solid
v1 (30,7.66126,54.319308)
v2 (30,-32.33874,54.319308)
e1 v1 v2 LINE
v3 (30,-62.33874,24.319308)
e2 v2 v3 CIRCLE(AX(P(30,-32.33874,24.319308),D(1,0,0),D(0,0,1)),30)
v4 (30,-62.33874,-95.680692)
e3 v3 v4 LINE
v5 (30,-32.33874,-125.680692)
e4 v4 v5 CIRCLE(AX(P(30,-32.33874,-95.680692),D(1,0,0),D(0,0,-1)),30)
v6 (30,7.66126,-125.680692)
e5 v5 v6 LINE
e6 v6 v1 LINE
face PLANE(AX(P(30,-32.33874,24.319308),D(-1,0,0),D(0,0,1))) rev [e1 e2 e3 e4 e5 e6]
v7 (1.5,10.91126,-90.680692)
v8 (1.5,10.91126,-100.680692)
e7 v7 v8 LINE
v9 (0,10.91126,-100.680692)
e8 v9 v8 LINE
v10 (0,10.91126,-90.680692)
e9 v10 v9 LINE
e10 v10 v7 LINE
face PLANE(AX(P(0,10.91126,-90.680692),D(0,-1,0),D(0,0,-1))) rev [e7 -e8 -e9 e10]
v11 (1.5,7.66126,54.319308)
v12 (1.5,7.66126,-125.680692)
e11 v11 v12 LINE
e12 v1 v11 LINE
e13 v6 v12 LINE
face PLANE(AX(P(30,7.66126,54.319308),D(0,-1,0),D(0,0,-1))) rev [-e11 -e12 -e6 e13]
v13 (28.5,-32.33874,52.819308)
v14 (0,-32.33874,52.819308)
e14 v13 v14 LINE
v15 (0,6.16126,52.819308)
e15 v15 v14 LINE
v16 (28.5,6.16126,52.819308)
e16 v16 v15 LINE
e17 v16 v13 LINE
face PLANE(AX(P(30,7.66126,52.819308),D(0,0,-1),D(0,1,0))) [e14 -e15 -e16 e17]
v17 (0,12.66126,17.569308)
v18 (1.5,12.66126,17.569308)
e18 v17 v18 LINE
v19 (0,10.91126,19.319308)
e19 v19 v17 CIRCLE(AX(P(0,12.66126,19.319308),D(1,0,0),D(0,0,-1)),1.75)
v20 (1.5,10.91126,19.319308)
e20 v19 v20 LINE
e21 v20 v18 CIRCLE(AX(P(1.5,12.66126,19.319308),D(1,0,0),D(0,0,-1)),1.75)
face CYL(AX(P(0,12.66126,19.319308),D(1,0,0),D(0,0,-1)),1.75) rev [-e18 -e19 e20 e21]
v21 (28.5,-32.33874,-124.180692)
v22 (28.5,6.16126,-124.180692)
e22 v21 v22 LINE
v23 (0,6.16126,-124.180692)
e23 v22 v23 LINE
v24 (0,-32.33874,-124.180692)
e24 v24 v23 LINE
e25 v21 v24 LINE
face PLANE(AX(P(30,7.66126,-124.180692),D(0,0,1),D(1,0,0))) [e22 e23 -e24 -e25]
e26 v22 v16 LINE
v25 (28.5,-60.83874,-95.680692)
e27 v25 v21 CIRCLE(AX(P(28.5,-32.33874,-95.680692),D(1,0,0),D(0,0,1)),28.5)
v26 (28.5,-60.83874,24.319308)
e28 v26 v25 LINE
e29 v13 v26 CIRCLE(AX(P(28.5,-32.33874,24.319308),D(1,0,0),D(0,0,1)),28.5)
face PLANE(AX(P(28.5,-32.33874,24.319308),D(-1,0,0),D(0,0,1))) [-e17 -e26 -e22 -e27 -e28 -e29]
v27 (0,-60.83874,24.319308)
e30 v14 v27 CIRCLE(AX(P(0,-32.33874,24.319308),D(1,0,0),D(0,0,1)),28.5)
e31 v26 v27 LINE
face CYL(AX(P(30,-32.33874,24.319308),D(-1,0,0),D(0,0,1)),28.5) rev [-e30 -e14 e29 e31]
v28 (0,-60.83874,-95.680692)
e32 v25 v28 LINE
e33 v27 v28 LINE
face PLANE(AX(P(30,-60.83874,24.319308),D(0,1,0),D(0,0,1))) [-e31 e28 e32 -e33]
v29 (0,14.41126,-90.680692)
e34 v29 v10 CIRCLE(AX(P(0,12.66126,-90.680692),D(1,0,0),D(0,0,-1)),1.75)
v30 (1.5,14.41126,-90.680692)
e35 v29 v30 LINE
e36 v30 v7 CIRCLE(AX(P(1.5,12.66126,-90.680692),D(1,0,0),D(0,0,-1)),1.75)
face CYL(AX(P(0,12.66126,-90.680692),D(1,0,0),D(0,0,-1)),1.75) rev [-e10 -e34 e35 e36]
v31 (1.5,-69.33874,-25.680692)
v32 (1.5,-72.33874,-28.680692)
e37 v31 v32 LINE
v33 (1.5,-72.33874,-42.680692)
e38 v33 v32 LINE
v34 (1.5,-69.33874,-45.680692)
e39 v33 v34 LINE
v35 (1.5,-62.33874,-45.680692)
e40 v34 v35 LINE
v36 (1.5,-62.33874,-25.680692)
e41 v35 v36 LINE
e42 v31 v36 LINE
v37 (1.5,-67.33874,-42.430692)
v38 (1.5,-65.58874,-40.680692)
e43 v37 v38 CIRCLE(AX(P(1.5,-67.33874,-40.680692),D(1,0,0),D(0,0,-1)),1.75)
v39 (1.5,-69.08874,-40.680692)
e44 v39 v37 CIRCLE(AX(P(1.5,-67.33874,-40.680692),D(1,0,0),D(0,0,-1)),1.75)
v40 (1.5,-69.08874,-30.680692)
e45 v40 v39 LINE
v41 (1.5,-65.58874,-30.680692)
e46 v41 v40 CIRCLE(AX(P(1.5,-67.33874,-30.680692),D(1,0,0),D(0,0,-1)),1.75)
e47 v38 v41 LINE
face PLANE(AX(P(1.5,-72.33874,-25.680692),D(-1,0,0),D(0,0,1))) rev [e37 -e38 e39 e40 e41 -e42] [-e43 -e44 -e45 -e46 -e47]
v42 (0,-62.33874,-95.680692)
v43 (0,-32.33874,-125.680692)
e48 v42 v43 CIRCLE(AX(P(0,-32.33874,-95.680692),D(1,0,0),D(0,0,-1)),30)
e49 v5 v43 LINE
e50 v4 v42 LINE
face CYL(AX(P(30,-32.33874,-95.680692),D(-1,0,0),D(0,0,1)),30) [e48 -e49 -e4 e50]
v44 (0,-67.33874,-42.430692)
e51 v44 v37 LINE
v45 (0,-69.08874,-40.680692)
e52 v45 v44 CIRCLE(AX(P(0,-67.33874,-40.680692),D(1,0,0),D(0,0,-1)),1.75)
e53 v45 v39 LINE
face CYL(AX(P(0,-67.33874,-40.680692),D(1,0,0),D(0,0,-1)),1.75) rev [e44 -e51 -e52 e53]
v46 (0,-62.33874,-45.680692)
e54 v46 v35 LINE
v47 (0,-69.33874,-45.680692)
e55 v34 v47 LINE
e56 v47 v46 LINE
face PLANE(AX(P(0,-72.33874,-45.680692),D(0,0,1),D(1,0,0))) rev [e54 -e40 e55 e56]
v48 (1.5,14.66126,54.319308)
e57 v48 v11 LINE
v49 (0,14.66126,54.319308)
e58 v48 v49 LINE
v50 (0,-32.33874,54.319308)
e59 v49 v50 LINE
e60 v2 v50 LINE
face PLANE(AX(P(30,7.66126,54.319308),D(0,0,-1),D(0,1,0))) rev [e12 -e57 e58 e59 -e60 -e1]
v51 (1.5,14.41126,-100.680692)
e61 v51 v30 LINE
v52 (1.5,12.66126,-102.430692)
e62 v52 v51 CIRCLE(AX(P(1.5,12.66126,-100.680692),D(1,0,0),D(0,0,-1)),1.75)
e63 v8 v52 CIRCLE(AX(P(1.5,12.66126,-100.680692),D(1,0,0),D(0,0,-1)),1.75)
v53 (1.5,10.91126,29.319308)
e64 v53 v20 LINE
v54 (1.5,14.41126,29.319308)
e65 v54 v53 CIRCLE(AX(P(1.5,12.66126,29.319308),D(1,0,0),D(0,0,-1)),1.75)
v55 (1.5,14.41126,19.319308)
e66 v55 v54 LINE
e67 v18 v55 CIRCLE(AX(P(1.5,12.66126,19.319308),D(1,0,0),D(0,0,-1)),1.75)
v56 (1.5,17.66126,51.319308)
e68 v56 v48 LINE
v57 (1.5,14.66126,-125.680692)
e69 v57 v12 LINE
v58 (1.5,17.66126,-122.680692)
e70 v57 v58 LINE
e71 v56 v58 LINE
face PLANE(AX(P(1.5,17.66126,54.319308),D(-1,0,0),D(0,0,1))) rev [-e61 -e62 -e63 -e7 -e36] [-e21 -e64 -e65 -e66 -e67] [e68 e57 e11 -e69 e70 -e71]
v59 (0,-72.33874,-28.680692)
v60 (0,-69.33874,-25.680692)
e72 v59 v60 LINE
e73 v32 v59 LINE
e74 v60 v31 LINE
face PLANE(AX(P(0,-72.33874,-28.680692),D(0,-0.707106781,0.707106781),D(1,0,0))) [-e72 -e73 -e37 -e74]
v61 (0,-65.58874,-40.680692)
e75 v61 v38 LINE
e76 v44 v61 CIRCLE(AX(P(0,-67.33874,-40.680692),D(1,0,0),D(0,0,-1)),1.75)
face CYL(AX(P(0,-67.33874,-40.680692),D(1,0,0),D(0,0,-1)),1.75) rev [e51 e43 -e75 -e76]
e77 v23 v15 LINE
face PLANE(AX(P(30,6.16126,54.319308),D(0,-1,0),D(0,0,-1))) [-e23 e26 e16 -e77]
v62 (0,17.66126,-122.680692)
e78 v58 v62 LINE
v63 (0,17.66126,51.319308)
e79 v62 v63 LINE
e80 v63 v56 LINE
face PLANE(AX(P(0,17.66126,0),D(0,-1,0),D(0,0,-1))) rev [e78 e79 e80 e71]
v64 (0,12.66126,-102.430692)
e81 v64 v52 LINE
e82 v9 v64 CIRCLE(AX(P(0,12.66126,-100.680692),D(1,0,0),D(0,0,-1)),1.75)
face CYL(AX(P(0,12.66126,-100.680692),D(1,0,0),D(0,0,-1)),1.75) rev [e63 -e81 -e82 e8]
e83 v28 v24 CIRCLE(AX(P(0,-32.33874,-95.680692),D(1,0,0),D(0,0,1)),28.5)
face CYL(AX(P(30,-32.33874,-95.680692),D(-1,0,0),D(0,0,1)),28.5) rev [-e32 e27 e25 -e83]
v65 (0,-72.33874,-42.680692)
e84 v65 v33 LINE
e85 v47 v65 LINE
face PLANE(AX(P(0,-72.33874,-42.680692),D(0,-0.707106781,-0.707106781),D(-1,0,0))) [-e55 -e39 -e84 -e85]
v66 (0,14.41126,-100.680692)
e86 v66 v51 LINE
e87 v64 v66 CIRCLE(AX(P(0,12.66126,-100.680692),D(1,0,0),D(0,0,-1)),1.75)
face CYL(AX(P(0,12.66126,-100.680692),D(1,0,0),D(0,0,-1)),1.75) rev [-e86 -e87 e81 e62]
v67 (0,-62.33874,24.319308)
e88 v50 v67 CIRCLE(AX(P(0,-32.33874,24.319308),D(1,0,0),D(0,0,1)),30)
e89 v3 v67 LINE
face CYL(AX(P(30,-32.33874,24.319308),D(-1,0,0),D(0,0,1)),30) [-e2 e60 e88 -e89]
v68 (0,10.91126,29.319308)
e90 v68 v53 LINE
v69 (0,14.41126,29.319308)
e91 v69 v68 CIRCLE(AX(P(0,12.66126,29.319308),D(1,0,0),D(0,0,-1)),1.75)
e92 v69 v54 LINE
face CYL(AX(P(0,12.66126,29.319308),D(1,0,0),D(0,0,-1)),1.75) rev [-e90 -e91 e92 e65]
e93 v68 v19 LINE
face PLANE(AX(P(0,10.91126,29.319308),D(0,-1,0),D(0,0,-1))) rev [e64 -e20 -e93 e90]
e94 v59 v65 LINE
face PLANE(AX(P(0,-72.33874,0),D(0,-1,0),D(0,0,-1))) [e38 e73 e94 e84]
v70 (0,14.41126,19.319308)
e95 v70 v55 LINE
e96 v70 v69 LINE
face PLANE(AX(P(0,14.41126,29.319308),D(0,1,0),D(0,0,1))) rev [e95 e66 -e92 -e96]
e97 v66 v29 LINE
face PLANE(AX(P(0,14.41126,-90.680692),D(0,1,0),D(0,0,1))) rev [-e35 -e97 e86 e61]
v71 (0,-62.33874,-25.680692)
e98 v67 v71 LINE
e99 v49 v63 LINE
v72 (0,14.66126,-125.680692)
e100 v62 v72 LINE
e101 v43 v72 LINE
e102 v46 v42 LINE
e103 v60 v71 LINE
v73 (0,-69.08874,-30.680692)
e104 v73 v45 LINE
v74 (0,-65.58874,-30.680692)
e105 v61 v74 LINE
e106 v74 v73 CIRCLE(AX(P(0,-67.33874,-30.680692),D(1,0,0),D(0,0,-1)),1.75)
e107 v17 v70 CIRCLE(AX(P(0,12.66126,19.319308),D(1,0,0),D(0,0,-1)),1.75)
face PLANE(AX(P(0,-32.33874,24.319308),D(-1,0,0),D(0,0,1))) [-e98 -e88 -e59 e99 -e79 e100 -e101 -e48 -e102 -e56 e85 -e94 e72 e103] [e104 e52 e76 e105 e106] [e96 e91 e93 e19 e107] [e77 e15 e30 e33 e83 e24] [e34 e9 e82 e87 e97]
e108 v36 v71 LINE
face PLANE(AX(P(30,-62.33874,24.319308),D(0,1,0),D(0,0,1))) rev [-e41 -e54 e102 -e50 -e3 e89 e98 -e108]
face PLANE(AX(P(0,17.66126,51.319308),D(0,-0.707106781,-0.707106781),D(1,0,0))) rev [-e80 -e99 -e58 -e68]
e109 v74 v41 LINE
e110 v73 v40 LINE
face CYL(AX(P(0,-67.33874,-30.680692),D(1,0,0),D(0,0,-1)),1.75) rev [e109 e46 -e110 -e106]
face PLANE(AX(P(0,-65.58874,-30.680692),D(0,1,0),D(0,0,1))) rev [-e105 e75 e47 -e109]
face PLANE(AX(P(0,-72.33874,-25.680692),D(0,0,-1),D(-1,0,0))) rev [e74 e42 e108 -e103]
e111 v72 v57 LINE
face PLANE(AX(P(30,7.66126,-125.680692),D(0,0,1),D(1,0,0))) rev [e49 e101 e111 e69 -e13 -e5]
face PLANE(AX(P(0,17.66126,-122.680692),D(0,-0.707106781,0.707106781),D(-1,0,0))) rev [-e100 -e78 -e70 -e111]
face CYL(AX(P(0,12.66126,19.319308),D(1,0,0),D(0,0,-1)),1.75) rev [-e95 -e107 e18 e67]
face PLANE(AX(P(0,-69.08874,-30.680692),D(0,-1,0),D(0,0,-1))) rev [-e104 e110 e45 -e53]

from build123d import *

# Parameters (mm, degrees)
EXTRUDE_1_DEPTH     = 30
SHELL_1_T           = -1.5
SKETCH_2_W          = 1.5
SKETCH_2_H          = 180
EXTRUDE_2_DEPTH     = 10
SKETCH_5_W          = 1.5
SKETCH_5_H          = 20
EXTRUDE_3_DEPTH     = 10
CUT_EXTRUDE_2_DEPTH = 148.786263339
CHAMFER_1_SIZE      = 3
CHAMFER_2_SIZE      = 3


with BuildPart() as part:
    # 草图1 → 凸台-拉伸1 (new body)
    with BuildSketch(Plane(origin=(0, 0, 0), x_dir=(0, 0, -1), z_dir=(1, 0, 0))):
        with BuildLine():
            Line((-54.319308007, 7.661260091), (125.680691993, 7.661260091))
            Line((125.680691993, 7.661260091), (125.680691993, -32.338739909))
            ThreePointArc((125.680691993, -32.338739909), (116.893895429, -53.551943345), (95.680691993, -62.338739909))
            Line((95.680691993, -62.338739909), (-24.319308007, -62.338739909))
            ThreePointArc((-24.319308007, -62.338739909), (-45.532511442, -53.551943345), (-54.319308007, -32.338739909))
            Line((-54.319308007, -32.338739909), (-54.319308007, 7.661260091))
        make_face()
    extrude(amount=EXTRUDE_1_DEPTH)

    # 抽壳1
    shell_1_openings = [part.faces().sort_by_distance(p)[0] for p in [
        (0, -26.44372844, -35.680691993),
    ]]
    offset(amount=SHELL_1_T, openings=shell_1_openings, kind=Kind.INTERSECTION)

    # 草图2 → 凸台-拉伸2 (add)
    with BuildSketch(Plane(origin=(0, 7.661260091, 0), x_dir=(1, 0, 0), z_dir=(0, 1, 0))):
        with Locations((0.75, 35.680691993)):
            Rectangle(SKETCH_2_W, SKETCH_2_H)
    extrude(amount=EXTRUDE_2_DEPTH)

    # 草图5 → 凸台-拉伸3 (add)
    with BuildSketch(Plane.XZ.offset(62.338739909)):
        with Locations((0.75, -35.680691993)):
            Rectangle(SKETCH_5_W, SKETCH_5_H)
    extrude(amount=EXTRUDE_3_DEPTH)

    # 草图4 → 切除-拉伸2 (cut, through all)
    with BuildSketch(Plane(origin=(1.5, 0, 0), x_dir=(0, 0, -1), z_dir=(1, 0, 0))):
        with BuildLine():
            Line((-29.319308007, 14.411260091), (-19.319308007, 14.411260091))
            ThreePointArc((-19.319308007, 14.411260091), (-17.569308007, 12.661260091), (-19.319308007, 10.911260091))
            Line((-19.319308007, 10.911260091), (-29.319308007, 10.911260091))
            ThreePointArc((-29.319308007, 10.911260091), (-31.069308007, 12.661260091), (-29.319308007, 14.411260091))
        make_face()
        with BuildLine():
            Line((90.680691993, 14.411260091), (100.680691993, 14.411260091))
            ThreePointArc((100.680691993, 14.411260091), (102.430691993, 12.661260091), (100.680691993, 10.911260091))
            Line((100.680691993, 10.911260091), (90.680691993, 10.911260091))
            ThreePointArc((90.680691993, 10.911260091), (88.930691993, 12.661260091), (90.680691993, 14.411260091))
        make_face()
        with BuildLine():
            Line((30.680691993, -65.588739909), (40.680691993, -65.588739909))
            ThreePointArc((40.680691993, -65.588739909), (42.430691993, -67.338739909), (40.680691993, -69.088739909))
            Line((40.680691993, -69.088739909), (30.680691993, -69.088739909))
            ThreePointArc((30.680691993, -69.088739909), (28.930691993, -67.338739909), (30.680691993, -65.588739909))
        make_face()
    extrude(amount=-CUT_EXTRUDE_2_DEPTH, mode=Mode.SUBTRACT)

    # 倒角1
    chamfer_1_edges = [part.edges().sort_by_distance(p)[0] for p in [
        (0.75, 17.661260091, -125.680691993),
        (0.75, 17.661260091, 54.319308007),
    ]]
    chamfer(chamfer_1_edges, length=CHAMFER_1_SIZE)

    # 倒角2
    chamfer_2_edges = [part.edges().sort_by_distance(p)[0] for p in [
        (0.75, -72.338739909, -45.680691993),
        (0.75, -72.338739909, -25.680691993),
    ]]
    chamfer(chamfer_2_edges, length=CHAMFER_2_SIZE)


solid = part.part
